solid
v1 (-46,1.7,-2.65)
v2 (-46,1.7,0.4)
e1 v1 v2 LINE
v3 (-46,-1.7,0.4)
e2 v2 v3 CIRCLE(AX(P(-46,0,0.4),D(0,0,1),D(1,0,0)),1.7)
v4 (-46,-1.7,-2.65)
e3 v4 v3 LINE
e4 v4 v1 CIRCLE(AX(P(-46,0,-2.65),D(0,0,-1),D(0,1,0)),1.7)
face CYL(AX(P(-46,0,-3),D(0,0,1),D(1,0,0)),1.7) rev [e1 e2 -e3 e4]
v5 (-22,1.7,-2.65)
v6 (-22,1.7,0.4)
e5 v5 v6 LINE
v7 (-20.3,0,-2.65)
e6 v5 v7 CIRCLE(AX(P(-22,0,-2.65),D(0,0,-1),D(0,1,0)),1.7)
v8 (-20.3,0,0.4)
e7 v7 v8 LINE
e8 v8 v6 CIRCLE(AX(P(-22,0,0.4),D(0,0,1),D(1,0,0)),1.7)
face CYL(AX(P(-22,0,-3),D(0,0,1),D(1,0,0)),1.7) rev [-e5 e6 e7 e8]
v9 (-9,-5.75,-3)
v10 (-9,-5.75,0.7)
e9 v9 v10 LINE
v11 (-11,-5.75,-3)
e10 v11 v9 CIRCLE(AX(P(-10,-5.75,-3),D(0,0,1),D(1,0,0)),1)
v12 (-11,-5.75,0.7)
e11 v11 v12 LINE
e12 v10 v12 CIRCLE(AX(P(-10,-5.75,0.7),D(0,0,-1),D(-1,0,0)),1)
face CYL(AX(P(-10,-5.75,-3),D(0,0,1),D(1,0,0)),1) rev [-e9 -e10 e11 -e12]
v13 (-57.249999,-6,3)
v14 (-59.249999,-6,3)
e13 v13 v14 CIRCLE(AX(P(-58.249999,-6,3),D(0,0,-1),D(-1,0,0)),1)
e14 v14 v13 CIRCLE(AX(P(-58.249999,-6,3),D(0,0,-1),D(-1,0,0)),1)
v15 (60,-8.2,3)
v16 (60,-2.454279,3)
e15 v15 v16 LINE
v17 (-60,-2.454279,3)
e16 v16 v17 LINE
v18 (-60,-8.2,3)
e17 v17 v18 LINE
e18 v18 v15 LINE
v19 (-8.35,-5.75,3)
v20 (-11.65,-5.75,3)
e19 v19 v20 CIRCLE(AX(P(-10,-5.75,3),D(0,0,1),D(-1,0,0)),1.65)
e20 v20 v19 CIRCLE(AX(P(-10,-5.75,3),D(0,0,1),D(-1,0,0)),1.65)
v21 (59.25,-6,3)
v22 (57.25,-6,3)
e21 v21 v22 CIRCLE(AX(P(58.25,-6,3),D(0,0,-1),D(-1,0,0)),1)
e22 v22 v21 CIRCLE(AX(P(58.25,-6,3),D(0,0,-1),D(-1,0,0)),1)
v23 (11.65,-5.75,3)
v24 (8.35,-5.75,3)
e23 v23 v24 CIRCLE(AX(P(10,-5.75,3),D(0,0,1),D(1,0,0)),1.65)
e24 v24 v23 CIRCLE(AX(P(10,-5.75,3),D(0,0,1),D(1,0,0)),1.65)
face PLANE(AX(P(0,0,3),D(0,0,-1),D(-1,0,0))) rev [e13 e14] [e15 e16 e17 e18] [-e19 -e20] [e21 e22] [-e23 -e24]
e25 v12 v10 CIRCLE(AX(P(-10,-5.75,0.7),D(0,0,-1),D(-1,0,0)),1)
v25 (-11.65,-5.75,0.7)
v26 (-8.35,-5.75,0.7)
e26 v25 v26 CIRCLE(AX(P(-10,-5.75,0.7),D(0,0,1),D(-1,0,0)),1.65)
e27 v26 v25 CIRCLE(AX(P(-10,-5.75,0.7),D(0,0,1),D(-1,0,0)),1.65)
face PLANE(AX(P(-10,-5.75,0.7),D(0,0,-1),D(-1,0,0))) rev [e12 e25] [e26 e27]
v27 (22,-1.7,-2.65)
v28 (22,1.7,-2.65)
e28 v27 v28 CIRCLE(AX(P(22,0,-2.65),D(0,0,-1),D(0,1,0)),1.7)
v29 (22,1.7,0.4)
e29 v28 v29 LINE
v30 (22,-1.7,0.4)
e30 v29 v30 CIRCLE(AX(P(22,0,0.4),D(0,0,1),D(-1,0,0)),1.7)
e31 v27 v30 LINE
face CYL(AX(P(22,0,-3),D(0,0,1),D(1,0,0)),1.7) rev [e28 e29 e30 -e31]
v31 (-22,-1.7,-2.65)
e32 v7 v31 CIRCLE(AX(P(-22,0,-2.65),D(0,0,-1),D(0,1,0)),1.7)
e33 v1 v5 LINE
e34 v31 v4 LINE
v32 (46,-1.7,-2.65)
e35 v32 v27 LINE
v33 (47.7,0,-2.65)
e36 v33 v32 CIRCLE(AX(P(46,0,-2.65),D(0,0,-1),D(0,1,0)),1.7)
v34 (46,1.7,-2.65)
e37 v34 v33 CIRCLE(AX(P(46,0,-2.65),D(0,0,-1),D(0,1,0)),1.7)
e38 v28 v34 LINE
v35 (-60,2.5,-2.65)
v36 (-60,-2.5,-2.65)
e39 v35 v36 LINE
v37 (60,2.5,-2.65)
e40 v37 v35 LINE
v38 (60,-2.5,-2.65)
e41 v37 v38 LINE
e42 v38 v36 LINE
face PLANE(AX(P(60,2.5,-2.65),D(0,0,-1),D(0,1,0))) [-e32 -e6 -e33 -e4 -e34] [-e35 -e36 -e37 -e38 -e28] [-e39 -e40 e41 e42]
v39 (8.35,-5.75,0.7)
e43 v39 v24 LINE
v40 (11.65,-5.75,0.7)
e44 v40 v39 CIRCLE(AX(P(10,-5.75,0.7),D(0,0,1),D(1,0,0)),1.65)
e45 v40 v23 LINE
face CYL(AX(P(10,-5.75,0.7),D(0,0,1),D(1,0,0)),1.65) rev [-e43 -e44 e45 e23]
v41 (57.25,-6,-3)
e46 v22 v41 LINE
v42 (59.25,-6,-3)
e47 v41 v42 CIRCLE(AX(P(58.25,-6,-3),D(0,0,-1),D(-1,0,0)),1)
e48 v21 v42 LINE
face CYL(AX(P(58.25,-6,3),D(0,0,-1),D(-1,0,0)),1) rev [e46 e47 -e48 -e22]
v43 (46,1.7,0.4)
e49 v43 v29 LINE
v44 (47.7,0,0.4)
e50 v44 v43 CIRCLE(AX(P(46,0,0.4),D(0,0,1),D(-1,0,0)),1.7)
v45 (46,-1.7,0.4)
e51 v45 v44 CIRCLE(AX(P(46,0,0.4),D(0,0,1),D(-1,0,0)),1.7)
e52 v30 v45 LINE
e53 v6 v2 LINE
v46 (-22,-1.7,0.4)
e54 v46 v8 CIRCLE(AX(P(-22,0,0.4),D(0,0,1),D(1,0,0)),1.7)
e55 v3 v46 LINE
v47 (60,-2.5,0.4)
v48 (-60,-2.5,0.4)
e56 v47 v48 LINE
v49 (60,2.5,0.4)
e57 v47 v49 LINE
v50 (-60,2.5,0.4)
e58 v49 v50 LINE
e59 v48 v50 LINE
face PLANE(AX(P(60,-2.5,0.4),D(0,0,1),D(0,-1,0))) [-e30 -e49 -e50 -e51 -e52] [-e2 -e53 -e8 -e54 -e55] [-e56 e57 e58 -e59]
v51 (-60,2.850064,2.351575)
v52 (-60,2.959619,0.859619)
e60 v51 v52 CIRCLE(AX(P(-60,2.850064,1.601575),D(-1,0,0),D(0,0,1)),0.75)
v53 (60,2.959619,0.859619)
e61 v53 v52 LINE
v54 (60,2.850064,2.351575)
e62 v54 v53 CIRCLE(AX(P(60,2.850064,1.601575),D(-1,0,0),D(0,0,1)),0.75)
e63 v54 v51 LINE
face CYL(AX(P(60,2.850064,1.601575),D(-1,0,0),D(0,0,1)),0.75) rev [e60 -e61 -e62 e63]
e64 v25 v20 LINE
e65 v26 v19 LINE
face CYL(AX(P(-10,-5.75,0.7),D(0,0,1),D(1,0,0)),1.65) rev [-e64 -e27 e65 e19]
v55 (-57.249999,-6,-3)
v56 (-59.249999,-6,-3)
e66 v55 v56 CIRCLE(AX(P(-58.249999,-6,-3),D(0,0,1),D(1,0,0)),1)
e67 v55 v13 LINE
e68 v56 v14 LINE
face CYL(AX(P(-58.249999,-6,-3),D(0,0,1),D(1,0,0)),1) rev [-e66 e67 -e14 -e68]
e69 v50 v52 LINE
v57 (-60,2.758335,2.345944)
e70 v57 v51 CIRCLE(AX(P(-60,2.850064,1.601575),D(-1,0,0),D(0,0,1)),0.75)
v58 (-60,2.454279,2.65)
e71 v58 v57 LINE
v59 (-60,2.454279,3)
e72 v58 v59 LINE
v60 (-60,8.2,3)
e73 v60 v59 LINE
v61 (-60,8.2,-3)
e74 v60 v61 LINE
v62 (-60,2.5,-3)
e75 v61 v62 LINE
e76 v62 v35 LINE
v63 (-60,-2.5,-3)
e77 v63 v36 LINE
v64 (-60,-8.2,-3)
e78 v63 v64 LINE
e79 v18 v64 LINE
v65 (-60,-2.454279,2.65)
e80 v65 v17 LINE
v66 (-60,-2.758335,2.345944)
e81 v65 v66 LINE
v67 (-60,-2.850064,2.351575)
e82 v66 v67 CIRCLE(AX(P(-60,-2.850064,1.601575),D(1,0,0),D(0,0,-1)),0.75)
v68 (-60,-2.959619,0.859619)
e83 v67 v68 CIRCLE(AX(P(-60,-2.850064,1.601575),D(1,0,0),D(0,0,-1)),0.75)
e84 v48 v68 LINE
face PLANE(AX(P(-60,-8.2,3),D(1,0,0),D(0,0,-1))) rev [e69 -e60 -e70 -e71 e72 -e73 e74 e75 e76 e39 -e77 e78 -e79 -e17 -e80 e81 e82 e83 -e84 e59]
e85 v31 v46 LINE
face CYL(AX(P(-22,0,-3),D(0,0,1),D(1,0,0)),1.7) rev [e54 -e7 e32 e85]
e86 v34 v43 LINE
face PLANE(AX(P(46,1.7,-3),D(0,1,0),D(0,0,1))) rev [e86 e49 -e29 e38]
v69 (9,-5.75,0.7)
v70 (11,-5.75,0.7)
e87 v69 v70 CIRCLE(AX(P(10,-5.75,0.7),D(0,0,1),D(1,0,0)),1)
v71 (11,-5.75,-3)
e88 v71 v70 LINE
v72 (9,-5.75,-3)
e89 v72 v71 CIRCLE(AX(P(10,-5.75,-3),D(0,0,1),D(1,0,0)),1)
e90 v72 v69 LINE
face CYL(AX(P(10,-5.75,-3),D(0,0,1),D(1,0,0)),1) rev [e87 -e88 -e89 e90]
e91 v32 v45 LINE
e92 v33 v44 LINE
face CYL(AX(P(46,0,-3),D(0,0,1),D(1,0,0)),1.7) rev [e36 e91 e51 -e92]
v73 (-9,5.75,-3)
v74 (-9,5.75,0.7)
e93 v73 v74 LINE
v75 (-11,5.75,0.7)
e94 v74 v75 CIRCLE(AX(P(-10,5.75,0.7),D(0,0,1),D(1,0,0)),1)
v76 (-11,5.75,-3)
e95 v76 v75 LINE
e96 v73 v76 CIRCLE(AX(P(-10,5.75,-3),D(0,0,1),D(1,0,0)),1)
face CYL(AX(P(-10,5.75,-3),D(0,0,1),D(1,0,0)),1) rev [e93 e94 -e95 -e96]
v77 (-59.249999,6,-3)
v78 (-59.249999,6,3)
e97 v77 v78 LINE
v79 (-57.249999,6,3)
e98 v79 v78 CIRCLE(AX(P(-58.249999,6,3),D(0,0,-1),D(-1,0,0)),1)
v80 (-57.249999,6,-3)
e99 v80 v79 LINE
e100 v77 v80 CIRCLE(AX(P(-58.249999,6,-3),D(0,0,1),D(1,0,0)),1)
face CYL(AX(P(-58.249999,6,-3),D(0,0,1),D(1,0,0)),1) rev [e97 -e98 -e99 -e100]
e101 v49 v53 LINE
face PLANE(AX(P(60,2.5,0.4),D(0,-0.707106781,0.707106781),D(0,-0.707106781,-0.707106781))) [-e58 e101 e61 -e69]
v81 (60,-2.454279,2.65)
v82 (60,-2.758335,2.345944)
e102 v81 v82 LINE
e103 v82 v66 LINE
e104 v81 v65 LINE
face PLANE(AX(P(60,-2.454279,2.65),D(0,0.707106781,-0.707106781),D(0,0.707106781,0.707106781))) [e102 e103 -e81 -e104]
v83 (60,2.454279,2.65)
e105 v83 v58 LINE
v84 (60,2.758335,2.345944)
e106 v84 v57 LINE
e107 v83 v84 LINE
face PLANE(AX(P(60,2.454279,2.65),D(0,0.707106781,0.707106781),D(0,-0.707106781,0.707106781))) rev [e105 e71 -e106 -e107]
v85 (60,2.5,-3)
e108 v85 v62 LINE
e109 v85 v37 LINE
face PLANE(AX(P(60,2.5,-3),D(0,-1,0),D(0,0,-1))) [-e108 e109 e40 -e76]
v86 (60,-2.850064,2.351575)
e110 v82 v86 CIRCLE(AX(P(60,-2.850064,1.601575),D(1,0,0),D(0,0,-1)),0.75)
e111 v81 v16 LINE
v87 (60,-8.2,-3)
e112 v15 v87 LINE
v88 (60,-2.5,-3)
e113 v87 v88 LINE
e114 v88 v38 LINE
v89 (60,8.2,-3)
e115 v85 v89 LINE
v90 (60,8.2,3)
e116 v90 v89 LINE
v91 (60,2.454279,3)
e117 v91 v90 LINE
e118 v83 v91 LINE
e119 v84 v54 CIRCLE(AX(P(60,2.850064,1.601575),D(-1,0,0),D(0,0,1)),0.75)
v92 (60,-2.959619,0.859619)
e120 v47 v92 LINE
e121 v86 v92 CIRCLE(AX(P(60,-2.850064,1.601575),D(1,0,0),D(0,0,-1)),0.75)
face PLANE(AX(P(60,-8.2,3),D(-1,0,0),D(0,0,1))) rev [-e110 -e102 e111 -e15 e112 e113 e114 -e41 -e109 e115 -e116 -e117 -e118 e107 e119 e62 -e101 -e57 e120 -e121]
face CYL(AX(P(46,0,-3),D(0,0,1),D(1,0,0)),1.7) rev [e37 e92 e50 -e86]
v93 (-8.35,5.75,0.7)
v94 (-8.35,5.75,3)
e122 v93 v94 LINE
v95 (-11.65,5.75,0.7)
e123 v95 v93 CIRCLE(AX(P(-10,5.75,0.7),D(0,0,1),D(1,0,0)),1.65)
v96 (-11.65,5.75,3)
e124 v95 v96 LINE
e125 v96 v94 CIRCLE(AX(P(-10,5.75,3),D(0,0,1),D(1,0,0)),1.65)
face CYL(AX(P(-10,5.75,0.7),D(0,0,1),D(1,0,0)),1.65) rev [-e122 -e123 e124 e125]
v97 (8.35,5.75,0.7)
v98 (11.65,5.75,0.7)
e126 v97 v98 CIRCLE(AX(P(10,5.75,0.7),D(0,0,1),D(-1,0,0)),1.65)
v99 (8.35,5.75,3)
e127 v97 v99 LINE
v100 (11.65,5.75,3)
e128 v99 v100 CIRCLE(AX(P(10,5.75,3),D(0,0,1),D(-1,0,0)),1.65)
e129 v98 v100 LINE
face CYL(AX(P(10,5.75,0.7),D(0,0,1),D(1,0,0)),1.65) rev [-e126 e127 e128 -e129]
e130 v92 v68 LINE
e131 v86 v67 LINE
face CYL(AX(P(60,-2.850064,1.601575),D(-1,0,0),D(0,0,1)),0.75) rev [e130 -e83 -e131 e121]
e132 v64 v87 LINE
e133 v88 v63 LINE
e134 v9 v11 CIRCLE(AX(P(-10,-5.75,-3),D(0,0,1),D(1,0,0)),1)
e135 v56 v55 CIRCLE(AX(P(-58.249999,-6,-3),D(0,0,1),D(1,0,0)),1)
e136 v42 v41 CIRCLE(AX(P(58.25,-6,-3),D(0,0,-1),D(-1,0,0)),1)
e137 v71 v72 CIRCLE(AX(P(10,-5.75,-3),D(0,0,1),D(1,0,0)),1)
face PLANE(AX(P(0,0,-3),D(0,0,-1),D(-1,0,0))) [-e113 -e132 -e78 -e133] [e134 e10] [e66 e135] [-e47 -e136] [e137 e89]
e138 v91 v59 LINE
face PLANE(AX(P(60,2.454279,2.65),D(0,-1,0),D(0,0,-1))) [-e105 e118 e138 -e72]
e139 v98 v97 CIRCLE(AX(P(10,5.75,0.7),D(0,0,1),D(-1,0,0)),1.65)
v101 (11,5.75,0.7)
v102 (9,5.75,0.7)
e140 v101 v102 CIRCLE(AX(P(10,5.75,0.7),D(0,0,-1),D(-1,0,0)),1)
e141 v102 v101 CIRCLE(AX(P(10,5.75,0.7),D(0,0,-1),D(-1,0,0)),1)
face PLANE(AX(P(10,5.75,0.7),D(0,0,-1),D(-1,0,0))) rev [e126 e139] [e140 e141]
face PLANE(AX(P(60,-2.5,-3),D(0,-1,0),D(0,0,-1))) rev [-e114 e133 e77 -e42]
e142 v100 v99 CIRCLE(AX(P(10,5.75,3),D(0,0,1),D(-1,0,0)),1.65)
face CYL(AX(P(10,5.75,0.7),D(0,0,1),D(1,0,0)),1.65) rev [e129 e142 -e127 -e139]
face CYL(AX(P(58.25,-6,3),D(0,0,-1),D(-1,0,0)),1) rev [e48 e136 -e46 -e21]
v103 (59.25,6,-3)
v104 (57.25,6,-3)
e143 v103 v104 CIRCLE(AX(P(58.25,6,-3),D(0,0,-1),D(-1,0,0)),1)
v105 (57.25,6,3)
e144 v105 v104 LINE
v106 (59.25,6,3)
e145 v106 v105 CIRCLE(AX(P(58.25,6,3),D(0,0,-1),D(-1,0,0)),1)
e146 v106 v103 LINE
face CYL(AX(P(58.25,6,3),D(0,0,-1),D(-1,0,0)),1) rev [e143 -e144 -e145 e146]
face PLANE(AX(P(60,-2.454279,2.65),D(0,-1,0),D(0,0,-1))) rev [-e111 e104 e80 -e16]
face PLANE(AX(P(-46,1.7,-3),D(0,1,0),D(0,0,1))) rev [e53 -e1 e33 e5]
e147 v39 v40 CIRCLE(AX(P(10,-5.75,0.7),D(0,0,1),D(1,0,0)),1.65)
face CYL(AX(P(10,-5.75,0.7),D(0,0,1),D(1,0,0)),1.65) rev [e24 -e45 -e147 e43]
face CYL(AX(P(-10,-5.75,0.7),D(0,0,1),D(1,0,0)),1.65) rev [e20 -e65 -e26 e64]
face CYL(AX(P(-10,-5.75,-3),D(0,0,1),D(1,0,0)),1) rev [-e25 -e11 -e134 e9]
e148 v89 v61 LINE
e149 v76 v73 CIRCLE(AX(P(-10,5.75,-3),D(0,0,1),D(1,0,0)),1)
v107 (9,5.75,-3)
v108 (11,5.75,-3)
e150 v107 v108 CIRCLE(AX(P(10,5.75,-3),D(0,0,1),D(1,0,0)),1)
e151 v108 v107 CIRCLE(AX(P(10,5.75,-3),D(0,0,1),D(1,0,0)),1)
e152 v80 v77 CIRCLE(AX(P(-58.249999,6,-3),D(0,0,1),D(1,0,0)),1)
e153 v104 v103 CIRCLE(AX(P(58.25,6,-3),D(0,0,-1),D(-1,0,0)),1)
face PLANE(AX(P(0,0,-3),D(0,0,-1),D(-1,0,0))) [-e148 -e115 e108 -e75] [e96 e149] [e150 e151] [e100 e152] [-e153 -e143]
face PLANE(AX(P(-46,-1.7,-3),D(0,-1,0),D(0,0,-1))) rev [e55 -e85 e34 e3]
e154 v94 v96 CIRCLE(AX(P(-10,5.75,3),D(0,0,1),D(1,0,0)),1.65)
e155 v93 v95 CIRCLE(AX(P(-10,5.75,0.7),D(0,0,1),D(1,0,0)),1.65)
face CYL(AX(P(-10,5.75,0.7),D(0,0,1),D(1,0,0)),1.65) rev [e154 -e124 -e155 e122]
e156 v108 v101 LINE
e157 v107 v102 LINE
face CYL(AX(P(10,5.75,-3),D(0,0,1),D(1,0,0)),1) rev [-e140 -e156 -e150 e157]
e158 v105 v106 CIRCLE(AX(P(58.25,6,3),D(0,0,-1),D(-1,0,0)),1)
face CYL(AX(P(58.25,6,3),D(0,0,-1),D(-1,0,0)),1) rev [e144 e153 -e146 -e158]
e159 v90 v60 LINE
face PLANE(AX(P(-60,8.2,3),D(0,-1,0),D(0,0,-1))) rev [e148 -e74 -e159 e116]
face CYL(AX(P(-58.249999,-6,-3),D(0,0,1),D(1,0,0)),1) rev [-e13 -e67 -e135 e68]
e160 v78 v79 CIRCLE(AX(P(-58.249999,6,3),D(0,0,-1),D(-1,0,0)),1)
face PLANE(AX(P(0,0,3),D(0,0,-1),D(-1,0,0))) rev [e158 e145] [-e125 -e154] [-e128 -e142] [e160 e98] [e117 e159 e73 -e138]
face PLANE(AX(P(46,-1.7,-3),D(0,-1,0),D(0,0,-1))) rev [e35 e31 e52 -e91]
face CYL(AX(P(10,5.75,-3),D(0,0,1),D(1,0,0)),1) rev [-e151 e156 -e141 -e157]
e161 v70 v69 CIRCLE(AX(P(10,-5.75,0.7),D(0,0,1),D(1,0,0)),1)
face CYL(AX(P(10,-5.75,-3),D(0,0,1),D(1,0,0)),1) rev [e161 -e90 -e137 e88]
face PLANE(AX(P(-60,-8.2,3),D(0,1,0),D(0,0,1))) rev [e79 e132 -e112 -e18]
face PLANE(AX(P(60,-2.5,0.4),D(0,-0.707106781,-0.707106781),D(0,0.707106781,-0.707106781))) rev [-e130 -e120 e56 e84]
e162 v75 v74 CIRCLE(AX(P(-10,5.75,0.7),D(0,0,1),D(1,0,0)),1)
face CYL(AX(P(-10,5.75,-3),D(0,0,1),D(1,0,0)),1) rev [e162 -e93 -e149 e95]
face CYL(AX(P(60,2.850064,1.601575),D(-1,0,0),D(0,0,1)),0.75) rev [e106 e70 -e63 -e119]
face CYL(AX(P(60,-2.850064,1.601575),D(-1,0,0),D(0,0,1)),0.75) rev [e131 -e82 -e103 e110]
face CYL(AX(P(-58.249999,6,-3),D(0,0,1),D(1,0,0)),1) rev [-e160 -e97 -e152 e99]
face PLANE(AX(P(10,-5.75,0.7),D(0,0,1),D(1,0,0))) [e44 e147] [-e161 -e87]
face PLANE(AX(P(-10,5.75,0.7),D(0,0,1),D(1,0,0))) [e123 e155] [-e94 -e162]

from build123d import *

# Parameters (mm, degrees)
SKETCH_1_W                = 120
SKETCH_1_H                = 16.4
EXTRUDE_1_DEPTH           = 3
SKETCH_2_R                = 1.65
SKETCH_2_R_2              = 1
CUT_EXTRUDE_2_DEPTH       = 2.3
SKETCH_3_R                = 1
CUT_EXTRUDE_3_DEPTH       = 61.854252111
SKETCH_4_W                = 0.35
SKETCH_4_H                = 5
CUT_EXTRUDE_5_DEPTH       = 121.317247309
CUT_EXTRUDE_6_DEPTH       = 61.653112039
CUT_EXTRUDE_7_DEPTH       = 61.854252111
CUT_EXTRUDE_7_DEPTH_BACK  = 61.854252111
SKETCH_7_R                = 1
CUT_EXTRUDE_10_DEPTH      = 61.854252111
CUT_EXTRUDE_10_DEPTH_BACK = 61.854252111
SKETCH_9_R                = 1


with BuildPart() as part:
    # 草图1 → 凸台-拉伸1 (new, symmetric)
    with BuildSketch(Plane.XY):
        Rectangle(SKETCH_1_W, SKETCH_1_H)
    extrude(amount=EXTRUDE_1_DEPTH, both=True)

    # 草图2 → 切除-拉伸2 (cut)
    # profile 1 of 4: a face of its own
    with BuildSketch(Plane.XY.offset(3)):
        with Locations((-10, 5.75)):
            Circle(SKETCH_2_R)
        with Locations((-10, 5.75)):
            Circle(SKETCH_2_R_2, mode=Mode.SUBTRACT)
    # profile 2 of 4: a face of its own
    with BuildSketch(Plane.XY.offset(3)):
        with Locations(Location((10, 5.75, 0), (0, 0, 180))):
            Circle(SKETCH_2_R)
        with Locations(Location((10, 5.75, 0), (0, 0, 180))):
            Circle(SKETCH_2_R_2, mode=Mode.SUBTRACT)
    # profile 3 of 4: a face of its own
    with BuildSketch(Plane.XY.offset(3)):
        with Locations((10, -5.75)):
            Circle(SKETCH_2_R)
        with Locations((10, -5.75)):
            Circle(SKETCH_2_R_2, mode=Mode.SUBTRACT)
    # profile 4 of 4: a face of its own
    with BuildSketch(Plane.XY.offset(3)):
        with Locations(Location((-10, -5.75, 0), (0, 0, 180))):
            Circle(SKETCH_2_R)
        with Locations(Location((-10, -5.75, 0), (0, 0, 180))):
            Circle(SKETCH_2_R_2, mode=Mode.SUBTRACT)
    extrude(amount=-CUT_EXTRUDE_2_DEPTH, mode=Mode.SUBTRACT)

    # 草图3 → 切除-拉伸3 (cut, through all)
    with BuildSketch(Plane.XY.offset(3)):
        with Locations((-10, 5.75)):
            Circle(SKETCH_3_R)
        with Locations((10, 5.75)):
            Circle(SKETCH_3_R)
        with Locations((-10, -5.75)):
            Circle(SKETCH_3_R)
        with Locations((10, -5.75)):
            Circle(SKETCH_3_R)
    extrude(amount=-CUT_EXTRUDE_3_DEPTH, mode=Mode.SUBTRACT)

    # 草图4 → 切除-拉伸5 (cut, through all)
    with BuildSketch(Plane.ZY.offset(60)):
        with Locations((-2.825, 0)):
            Rectangle(SKETCH_4_W, SKETCH_4_H)
        with BuildLine():
            Line((0.4, -2.5), (0.4, 2.5))
            Line((0.4, 2.5), (0.859619408, 2.959619408))
            ThreePointArc((0.859619408, 2.959619408), (1.702223965, 3.593279549), (2.345944084, 2.758335226))
            Line((2.345944084, 2.758335226), (2.65, 2.45427931))
            Line((2.65, 2.45427931), (3, 2.45427931))
            Line((3, 2.45427931), (3, -2.45427931))
            Line((3, -2.45427931), (2.65, -2.45427931))
            Line((2.65, -2.45427931), (2.345944084, -2.758335226))
            ThreePointArc((2.345944084, -2.758335226), (1.702223965, -3.593279549), (0.859619408, -2.959619408))
            Line((0.859619408, -2.959619408), (0.4, -2.5))
        make_face()
    extrude(amount=-CUT_EXTRUDE_5_DEPTH, mode=Mode.SUBTRACT)

    # 草图5 → 切除-拉伸6 (cut, through all)
    with BuildSketch(Plane.XY.offset(0.4)):
        with BuildLine():
            Line((-46, 1.7), (-22, 1.7))
            ThreePointArc((-22, 1.7), (-20.3, 0), (-22, -1.7))
            Line((-22, -1.7), (-46, -1.7))
            ThreePointArc((-46, -1.7), (-47.7, 0), (-46, 1.7))
        make_face()
        with BuildLine():
            Line((46, 1.7), (22, 1.7))
            ThreePointArc((22, 1.7), (20.3, 0), (22, -1.7))
            Line((22, -1.7), (46, -1.7))
            ThreePointArc((46, -1.7), (47.7, 0), (46, 1.7))
        make_face()
    extrude(amount=-CUT_EXTRUDE_6_DEPTH, mode=Mode.SUBTRACT)

    # 草图7 → 切除-拉伸7 (cut, two sides: drawn at the far end of the back side and taken through both)
    with BuildSketch(Plane(origin=(0, 0, -3), x_dir=(-1, 0, 0), z_dir=(0, 0, -1)).offset(-CUT_EXTRUDE_7_DEPTH_BACK)):
        with Locations((-58.249999998, -6)):
            Circle(SKETCH_7_R)
        with Locations((-58.249999998, 6)):
            Circle(SKETCH_7_R)
    extrude(amount=CUT_EXTRUDE_7_DEPTH + CUT_EXTRUDE_7_DEPTH_BACK, mode=Mode.SUBTRACT)

    # 草图9 → 切除-拉伸10 (cut, two sides: drawn at the far end of the back side and taken through both)
    with BuildSketch(Plane.XY.offset(3).offset(-CUT_EXTRUDE_10_DEPTH_BACK)):
        with Locations((-58.249989067, 5.99999379)):
            Circle(SKETCH_9_R)
        with Locations((-58.249989067, -6.00000621)):
            Circle(SKETCH_9_R)
    extrude(amount=CUT_EXTRUDE_10_DEPTH + CUT_EXTRUDE_10_DEPTH_BACK, mode=Mode.SUBTRACT)


solid = part.part
